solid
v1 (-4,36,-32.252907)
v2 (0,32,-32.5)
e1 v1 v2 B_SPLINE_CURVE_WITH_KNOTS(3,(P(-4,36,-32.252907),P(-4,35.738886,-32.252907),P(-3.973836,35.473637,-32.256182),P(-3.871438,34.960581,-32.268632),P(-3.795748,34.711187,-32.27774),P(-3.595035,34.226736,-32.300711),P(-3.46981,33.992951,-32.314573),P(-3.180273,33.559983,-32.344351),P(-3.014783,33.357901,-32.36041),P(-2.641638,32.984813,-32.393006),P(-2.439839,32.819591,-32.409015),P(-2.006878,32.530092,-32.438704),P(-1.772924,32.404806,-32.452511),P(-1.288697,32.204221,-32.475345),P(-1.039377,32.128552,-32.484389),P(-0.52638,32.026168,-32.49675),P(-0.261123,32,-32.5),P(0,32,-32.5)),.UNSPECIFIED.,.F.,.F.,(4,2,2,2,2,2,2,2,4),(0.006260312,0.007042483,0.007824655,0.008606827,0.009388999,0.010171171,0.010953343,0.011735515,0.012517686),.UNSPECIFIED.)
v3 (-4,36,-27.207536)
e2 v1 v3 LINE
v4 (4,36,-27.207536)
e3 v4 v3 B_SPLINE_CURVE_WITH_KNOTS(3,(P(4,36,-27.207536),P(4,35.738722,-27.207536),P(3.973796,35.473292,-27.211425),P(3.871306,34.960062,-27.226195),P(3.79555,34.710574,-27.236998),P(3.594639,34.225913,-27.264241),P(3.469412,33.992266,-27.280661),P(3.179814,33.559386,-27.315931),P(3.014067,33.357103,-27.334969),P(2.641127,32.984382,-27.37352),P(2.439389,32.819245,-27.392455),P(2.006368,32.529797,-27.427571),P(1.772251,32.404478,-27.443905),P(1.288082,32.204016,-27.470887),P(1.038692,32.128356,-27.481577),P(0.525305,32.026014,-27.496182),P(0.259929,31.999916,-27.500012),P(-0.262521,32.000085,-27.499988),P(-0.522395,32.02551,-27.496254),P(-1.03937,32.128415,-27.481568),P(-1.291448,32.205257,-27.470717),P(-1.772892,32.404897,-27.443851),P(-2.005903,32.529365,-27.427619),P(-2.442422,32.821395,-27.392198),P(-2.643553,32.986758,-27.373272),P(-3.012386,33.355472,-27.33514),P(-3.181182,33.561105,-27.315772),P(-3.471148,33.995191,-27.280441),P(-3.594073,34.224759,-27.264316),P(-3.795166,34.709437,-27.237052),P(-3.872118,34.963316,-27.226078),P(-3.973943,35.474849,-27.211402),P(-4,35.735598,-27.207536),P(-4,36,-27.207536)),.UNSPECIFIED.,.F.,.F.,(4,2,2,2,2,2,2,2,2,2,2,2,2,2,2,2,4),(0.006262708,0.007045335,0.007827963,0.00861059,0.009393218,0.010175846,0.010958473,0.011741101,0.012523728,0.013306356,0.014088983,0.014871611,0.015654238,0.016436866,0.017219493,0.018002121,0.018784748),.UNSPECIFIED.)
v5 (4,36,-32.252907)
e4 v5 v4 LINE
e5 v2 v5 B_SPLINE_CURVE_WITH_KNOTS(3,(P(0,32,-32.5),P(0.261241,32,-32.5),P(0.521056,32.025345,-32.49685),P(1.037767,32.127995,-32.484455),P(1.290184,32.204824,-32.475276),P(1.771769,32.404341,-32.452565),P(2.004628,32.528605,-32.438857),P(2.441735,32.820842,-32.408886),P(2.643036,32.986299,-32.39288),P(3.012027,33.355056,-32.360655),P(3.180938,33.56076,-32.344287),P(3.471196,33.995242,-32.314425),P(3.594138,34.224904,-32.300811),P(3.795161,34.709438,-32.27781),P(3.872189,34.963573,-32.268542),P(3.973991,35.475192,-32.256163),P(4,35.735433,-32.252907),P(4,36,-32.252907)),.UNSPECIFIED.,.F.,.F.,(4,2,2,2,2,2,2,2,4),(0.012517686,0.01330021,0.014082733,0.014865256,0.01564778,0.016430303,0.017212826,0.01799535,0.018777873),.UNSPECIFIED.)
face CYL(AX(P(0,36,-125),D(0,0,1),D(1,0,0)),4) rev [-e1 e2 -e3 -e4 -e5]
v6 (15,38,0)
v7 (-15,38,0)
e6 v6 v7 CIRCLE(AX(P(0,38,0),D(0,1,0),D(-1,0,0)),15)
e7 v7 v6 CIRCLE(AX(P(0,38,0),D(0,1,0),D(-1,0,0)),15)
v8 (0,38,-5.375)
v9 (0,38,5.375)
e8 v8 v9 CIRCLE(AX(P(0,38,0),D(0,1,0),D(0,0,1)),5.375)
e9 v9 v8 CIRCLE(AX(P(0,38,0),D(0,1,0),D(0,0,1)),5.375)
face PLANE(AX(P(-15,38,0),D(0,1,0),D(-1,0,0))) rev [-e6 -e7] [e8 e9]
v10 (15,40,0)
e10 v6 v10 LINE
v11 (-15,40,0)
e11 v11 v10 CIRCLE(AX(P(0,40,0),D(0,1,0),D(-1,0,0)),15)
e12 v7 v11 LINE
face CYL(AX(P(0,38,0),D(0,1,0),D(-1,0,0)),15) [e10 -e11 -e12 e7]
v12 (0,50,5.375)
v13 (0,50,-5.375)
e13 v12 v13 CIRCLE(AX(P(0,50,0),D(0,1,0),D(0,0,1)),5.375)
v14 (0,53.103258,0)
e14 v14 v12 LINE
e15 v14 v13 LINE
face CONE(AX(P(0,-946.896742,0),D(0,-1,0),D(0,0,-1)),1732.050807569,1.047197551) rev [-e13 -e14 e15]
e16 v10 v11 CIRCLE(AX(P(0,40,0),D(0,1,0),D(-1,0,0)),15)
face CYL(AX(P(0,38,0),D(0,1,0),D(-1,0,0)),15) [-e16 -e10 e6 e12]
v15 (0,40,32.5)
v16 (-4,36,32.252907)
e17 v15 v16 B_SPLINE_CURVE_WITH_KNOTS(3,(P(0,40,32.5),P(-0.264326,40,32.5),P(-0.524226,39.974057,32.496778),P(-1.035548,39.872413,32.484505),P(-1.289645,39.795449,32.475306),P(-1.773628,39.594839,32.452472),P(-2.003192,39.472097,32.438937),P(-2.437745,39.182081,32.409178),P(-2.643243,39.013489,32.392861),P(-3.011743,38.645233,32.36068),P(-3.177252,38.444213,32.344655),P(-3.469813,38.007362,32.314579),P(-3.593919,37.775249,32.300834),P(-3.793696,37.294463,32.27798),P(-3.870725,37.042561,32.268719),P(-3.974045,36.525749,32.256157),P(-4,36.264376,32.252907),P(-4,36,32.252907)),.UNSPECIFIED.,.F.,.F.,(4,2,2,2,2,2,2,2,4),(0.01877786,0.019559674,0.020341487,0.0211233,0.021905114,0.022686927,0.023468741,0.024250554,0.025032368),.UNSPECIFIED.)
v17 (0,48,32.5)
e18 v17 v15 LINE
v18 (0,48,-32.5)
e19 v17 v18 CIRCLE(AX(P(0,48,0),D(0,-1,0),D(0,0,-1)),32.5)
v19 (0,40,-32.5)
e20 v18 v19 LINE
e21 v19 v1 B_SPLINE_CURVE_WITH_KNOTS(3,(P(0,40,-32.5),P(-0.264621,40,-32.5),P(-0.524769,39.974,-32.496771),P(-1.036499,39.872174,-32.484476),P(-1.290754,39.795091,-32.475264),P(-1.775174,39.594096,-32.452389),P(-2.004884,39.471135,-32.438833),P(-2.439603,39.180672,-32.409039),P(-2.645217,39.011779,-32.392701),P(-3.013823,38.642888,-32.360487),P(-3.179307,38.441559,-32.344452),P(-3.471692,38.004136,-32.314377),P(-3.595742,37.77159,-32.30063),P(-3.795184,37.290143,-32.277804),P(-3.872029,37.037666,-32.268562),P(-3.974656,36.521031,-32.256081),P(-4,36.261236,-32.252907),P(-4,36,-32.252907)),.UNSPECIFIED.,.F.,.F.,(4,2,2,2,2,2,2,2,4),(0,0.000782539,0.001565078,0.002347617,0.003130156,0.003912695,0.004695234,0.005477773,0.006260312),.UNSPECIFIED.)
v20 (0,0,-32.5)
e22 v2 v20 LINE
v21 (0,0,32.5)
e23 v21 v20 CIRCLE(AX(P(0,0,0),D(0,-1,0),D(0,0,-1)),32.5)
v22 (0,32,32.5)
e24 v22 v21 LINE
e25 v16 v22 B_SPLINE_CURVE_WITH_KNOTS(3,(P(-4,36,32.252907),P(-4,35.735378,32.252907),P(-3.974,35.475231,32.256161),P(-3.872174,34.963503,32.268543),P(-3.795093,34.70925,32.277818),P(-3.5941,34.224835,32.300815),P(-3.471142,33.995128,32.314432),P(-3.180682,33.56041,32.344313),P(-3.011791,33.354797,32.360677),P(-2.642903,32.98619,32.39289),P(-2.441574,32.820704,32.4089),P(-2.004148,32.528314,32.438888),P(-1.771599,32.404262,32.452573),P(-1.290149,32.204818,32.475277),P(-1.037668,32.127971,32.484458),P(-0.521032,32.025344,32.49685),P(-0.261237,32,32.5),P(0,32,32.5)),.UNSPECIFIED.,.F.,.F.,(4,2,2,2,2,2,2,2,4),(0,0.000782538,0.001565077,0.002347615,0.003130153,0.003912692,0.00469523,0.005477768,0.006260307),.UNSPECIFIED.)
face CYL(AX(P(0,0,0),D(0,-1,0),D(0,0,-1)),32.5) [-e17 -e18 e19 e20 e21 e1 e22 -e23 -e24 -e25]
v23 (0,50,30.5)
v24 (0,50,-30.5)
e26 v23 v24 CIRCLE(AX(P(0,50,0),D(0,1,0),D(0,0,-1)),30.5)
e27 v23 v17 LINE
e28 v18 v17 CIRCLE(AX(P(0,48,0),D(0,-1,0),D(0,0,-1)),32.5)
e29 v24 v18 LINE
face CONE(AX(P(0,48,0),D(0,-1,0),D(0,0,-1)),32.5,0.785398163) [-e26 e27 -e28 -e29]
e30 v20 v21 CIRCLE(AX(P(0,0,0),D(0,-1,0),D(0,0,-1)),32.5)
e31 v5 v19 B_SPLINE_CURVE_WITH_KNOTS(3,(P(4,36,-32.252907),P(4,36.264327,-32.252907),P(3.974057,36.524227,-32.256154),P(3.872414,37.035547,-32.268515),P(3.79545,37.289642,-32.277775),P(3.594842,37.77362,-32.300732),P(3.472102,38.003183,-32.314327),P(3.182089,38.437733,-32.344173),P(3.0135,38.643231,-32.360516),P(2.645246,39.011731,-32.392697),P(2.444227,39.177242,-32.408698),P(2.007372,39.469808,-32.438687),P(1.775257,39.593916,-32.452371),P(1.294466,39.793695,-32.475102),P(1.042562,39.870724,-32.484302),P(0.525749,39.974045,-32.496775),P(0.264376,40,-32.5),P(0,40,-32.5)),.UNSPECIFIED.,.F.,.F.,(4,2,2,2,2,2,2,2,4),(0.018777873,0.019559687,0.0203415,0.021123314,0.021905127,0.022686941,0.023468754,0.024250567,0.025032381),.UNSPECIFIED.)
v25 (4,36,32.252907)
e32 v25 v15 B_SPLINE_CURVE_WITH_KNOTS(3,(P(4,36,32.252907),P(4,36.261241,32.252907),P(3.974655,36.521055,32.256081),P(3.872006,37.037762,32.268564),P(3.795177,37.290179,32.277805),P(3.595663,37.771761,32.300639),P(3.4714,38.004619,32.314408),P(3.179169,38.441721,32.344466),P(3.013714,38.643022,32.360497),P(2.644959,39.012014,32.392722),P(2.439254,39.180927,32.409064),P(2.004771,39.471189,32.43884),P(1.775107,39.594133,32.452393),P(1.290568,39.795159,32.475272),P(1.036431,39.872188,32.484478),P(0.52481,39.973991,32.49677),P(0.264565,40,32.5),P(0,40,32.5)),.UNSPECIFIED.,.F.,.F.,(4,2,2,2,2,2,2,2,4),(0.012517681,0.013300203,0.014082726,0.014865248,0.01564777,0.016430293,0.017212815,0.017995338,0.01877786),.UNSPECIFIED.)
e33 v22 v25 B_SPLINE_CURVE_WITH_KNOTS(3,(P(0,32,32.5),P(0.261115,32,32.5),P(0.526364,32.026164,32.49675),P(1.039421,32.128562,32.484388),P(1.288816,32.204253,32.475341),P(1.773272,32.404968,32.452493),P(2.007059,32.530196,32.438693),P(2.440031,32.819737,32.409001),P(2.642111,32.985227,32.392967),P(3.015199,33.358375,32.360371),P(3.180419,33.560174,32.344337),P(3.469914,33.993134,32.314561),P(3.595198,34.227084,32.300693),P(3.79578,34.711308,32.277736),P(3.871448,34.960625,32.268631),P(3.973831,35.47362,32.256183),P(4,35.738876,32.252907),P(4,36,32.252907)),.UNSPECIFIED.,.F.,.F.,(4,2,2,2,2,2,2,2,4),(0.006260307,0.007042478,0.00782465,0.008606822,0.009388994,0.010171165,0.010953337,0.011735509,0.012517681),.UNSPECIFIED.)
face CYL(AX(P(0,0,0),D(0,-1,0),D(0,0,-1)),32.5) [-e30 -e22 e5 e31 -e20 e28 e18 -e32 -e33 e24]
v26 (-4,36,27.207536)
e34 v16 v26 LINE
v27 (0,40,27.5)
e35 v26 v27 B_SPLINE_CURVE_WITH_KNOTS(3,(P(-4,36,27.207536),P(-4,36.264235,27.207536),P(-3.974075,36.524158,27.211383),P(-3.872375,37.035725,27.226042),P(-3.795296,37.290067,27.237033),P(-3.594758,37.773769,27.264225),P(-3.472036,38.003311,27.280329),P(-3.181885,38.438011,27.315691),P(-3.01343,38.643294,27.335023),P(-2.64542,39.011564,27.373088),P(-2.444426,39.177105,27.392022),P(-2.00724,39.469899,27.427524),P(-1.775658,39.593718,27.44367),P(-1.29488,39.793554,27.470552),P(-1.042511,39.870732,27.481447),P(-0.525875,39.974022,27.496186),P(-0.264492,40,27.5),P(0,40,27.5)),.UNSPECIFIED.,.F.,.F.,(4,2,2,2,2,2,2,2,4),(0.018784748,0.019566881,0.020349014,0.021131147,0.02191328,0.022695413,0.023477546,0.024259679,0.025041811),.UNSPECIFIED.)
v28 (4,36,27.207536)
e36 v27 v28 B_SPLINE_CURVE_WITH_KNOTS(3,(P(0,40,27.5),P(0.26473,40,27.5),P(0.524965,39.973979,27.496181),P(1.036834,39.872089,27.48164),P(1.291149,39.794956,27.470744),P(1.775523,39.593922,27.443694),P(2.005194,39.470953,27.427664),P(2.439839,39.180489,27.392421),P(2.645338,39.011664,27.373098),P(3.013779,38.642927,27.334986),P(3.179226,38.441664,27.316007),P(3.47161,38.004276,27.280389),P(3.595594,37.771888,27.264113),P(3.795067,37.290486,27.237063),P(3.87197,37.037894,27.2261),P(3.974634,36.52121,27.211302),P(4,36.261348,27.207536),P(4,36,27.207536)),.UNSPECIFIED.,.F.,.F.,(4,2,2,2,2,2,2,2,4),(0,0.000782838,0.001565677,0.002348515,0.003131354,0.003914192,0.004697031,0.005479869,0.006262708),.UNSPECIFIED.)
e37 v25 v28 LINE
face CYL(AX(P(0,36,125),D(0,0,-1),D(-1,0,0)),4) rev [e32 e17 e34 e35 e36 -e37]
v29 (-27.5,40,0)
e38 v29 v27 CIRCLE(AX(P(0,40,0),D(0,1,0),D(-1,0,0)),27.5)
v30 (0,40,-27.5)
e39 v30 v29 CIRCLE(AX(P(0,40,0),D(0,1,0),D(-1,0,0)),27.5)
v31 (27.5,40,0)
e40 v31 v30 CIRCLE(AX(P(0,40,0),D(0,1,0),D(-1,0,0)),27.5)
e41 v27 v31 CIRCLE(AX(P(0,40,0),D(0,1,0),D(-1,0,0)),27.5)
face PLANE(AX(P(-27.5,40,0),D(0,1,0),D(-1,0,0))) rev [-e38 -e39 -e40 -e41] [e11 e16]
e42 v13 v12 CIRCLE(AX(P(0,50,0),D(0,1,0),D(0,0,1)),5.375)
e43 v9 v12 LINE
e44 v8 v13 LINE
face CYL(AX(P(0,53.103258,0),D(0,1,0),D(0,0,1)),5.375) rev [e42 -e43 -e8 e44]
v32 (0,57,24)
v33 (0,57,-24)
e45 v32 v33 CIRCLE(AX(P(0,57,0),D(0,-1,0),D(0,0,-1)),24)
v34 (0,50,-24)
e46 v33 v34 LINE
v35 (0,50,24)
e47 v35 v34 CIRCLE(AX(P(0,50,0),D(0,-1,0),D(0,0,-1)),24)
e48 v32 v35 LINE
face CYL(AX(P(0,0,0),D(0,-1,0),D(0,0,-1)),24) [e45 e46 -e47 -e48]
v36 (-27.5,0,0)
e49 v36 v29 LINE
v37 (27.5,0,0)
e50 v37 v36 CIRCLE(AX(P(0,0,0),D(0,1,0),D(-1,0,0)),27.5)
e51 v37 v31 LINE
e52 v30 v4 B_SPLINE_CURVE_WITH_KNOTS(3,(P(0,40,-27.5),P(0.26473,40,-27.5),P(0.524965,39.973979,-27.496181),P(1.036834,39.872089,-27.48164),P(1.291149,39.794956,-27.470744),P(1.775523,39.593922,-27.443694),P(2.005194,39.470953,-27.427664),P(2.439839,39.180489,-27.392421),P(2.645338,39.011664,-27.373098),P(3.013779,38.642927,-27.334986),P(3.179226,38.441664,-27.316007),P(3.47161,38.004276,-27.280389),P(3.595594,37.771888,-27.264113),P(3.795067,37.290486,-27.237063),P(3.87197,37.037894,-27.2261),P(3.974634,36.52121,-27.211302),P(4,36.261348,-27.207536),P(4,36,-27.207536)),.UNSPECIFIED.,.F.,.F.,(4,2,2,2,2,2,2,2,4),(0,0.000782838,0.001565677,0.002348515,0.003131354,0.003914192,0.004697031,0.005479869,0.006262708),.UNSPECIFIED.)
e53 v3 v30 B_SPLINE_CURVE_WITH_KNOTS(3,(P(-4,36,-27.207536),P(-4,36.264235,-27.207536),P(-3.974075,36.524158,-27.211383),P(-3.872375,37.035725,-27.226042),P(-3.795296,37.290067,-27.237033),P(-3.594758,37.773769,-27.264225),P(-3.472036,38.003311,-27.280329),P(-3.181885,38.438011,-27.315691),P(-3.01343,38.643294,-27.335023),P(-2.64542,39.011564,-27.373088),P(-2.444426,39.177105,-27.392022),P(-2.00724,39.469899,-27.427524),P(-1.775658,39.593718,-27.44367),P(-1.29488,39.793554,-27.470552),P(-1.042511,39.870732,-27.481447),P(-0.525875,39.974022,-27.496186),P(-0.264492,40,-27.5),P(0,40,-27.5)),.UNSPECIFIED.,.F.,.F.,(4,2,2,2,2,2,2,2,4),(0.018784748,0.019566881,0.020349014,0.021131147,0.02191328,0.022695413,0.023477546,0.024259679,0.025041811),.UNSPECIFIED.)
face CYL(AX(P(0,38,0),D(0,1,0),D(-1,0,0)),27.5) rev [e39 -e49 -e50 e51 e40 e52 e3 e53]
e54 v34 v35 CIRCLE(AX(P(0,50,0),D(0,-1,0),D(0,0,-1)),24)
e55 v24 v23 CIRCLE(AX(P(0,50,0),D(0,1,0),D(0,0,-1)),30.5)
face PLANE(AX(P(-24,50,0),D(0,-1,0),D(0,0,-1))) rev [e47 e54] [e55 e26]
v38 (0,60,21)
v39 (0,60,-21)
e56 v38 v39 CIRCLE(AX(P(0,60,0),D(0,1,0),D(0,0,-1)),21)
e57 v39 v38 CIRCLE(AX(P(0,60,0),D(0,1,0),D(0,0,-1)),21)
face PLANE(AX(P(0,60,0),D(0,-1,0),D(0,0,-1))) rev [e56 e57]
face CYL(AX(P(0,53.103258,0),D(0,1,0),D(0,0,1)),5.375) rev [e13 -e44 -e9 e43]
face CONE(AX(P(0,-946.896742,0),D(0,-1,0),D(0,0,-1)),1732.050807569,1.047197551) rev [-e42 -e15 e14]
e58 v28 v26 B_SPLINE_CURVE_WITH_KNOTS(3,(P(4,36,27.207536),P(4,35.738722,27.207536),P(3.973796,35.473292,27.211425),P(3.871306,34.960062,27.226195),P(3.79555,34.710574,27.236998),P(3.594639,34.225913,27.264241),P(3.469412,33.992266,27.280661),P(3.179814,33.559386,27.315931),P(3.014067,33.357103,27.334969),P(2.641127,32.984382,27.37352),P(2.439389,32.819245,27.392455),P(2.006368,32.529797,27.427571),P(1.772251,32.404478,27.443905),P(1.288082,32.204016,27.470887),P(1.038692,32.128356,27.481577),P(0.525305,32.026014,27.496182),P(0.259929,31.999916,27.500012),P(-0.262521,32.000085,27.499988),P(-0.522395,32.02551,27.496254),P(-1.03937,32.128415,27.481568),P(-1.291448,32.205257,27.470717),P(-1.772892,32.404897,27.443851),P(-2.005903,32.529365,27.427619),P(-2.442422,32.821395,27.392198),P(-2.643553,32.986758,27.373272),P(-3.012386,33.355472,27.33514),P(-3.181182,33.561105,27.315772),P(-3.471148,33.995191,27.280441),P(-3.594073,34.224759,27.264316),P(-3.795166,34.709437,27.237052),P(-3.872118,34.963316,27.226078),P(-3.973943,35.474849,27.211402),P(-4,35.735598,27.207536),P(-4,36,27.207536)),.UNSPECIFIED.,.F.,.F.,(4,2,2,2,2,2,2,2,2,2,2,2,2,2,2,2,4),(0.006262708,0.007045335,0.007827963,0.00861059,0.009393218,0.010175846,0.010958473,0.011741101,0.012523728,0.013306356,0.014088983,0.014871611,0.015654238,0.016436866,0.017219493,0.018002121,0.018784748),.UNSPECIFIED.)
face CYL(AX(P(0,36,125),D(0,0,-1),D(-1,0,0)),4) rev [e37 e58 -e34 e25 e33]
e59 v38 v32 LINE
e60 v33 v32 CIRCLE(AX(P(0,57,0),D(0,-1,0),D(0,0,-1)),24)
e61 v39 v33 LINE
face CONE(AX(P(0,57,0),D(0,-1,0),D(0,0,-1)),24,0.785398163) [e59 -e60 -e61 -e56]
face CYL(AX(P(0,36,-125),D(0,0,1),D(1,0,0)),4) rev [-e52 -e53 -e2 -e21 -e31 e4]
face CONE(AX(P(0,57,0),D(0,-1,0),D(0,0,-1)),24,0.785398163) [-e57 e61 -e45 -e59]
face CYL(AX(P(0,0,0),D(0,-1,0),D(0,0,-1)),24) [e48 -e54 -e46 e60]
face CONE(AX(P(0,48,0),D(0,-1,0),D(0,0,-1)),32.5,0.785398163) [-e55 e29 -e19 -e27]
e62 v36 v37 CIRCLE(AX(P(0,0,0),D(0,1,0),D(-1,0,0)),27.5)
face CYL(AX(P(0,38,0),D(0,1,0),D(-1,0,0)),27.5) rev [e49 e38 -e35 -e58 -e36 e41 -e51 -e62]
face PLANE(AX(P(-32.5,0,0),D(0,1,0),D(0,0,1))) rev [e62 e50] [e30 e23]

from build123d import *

# Parameters (mm, degrees)
CHAMFER1_SIZE      = 3
CHAMFER2_SIZE      = 2
CUT_EXTRUDE1_START = -20
SKETCH3_R          = 4
CUT_EXTRUDE1_DEPTH = 105
CUT_EXTRUDE2_START = 125
SKETCH4_R          = 4
CUT_EXTRUDE2_DEPTH = 105


with BuildPart() as part:
    # Sketch1 → Revolve1 (revolve)
    with BuildSketch(Plane.XY, mode=Mode.PRIVATE) as revolve1_sk:
        Polygon((0, 60), (-24, 60), (-24, 50), (-32.5, 50), (-32.5, 0), (0, 0), align=None)
    revolve(revolve1_sk.sketch.rotate(Axis((0, 0, 0), (0, 1, 0)), 270), axis=Axis((0, 0, 0), (0, 1, 0)))

    # Chamfer1
    chamfer1_edges = [part.edges().sort_by_distance(p)[0] for p in [
        (0, 60, 24),
    ]]
    chamfer(chamfer1_edges, length=CHAMFER1_SIZE)

    # Chamfer2
    chamfer2_edges = [part.edges().sort_by_distance(p)[0] for p in [
        (0, 50, 32.5),
    ]]
    chamfer(chamfer2_edges, length=CHAMFER2_SIZE)

    # Sketch2 → Cut-Revolve1 (revolve, cut)
    with BuildSketch(Plane.XY):
        Polygon((-27.5, 0), (-27.5, 40), (-15, 40), (-15, 38), (0, 38), (0, 0), align=None)
    revolve(axis=Axis((0, 38, 0), (0, -1, 0)), mode=Mode.SUBTRACT)

    # Sketch3 → Cut-Extrude1 (cut)
    with BuildSketch(Plane.XY.offset(CUT_EXTRUDE1_START)):
        with Locations(Location((0, 36, 0), (0, 0, 90))):
            Circle(SKETCH3_R)
    extrude(amount=-CUT_EXTRUDE1_DEPTH, mode=Mode.SUBTRACT)

    # Sketch4 → Cut-Extrude2 (cut)
    with BuildSketch(Plane.XY.offset(CUT_EXTRUDE2_START)):
        with Locations(Location((0, 36, 0), (0, 0, 90))):
            Circle(SKETCH4_R)
    extrude(amount=-CUT_EXTRUDE2_DEPTH, mode=Mode.SUBTRACT)

    # Sketch7 → Cut-Revolve2 (revolve, cut)
    with BuildSketch(Plane(origin=(0, 0, 0), x_dir=(0, 0, -1), z_dir=(1, 0, 0)), mode=Mode.PRIVATE) as cut_revolve2_sk:
        Polygon((-5.375, 38), (-5.375, 50), (0, 53.103257697), (0, 38), align=None)
    revolve(cut_revolve2_sk.sketch.rotate(Axis((0, 53.103257697, 0), (0, -1, 0)), 180), axis=Axis((0, 53.103257697, 0), (0, -1, 0)), mode=Mode.SUBTRACT)


solid = part.part
